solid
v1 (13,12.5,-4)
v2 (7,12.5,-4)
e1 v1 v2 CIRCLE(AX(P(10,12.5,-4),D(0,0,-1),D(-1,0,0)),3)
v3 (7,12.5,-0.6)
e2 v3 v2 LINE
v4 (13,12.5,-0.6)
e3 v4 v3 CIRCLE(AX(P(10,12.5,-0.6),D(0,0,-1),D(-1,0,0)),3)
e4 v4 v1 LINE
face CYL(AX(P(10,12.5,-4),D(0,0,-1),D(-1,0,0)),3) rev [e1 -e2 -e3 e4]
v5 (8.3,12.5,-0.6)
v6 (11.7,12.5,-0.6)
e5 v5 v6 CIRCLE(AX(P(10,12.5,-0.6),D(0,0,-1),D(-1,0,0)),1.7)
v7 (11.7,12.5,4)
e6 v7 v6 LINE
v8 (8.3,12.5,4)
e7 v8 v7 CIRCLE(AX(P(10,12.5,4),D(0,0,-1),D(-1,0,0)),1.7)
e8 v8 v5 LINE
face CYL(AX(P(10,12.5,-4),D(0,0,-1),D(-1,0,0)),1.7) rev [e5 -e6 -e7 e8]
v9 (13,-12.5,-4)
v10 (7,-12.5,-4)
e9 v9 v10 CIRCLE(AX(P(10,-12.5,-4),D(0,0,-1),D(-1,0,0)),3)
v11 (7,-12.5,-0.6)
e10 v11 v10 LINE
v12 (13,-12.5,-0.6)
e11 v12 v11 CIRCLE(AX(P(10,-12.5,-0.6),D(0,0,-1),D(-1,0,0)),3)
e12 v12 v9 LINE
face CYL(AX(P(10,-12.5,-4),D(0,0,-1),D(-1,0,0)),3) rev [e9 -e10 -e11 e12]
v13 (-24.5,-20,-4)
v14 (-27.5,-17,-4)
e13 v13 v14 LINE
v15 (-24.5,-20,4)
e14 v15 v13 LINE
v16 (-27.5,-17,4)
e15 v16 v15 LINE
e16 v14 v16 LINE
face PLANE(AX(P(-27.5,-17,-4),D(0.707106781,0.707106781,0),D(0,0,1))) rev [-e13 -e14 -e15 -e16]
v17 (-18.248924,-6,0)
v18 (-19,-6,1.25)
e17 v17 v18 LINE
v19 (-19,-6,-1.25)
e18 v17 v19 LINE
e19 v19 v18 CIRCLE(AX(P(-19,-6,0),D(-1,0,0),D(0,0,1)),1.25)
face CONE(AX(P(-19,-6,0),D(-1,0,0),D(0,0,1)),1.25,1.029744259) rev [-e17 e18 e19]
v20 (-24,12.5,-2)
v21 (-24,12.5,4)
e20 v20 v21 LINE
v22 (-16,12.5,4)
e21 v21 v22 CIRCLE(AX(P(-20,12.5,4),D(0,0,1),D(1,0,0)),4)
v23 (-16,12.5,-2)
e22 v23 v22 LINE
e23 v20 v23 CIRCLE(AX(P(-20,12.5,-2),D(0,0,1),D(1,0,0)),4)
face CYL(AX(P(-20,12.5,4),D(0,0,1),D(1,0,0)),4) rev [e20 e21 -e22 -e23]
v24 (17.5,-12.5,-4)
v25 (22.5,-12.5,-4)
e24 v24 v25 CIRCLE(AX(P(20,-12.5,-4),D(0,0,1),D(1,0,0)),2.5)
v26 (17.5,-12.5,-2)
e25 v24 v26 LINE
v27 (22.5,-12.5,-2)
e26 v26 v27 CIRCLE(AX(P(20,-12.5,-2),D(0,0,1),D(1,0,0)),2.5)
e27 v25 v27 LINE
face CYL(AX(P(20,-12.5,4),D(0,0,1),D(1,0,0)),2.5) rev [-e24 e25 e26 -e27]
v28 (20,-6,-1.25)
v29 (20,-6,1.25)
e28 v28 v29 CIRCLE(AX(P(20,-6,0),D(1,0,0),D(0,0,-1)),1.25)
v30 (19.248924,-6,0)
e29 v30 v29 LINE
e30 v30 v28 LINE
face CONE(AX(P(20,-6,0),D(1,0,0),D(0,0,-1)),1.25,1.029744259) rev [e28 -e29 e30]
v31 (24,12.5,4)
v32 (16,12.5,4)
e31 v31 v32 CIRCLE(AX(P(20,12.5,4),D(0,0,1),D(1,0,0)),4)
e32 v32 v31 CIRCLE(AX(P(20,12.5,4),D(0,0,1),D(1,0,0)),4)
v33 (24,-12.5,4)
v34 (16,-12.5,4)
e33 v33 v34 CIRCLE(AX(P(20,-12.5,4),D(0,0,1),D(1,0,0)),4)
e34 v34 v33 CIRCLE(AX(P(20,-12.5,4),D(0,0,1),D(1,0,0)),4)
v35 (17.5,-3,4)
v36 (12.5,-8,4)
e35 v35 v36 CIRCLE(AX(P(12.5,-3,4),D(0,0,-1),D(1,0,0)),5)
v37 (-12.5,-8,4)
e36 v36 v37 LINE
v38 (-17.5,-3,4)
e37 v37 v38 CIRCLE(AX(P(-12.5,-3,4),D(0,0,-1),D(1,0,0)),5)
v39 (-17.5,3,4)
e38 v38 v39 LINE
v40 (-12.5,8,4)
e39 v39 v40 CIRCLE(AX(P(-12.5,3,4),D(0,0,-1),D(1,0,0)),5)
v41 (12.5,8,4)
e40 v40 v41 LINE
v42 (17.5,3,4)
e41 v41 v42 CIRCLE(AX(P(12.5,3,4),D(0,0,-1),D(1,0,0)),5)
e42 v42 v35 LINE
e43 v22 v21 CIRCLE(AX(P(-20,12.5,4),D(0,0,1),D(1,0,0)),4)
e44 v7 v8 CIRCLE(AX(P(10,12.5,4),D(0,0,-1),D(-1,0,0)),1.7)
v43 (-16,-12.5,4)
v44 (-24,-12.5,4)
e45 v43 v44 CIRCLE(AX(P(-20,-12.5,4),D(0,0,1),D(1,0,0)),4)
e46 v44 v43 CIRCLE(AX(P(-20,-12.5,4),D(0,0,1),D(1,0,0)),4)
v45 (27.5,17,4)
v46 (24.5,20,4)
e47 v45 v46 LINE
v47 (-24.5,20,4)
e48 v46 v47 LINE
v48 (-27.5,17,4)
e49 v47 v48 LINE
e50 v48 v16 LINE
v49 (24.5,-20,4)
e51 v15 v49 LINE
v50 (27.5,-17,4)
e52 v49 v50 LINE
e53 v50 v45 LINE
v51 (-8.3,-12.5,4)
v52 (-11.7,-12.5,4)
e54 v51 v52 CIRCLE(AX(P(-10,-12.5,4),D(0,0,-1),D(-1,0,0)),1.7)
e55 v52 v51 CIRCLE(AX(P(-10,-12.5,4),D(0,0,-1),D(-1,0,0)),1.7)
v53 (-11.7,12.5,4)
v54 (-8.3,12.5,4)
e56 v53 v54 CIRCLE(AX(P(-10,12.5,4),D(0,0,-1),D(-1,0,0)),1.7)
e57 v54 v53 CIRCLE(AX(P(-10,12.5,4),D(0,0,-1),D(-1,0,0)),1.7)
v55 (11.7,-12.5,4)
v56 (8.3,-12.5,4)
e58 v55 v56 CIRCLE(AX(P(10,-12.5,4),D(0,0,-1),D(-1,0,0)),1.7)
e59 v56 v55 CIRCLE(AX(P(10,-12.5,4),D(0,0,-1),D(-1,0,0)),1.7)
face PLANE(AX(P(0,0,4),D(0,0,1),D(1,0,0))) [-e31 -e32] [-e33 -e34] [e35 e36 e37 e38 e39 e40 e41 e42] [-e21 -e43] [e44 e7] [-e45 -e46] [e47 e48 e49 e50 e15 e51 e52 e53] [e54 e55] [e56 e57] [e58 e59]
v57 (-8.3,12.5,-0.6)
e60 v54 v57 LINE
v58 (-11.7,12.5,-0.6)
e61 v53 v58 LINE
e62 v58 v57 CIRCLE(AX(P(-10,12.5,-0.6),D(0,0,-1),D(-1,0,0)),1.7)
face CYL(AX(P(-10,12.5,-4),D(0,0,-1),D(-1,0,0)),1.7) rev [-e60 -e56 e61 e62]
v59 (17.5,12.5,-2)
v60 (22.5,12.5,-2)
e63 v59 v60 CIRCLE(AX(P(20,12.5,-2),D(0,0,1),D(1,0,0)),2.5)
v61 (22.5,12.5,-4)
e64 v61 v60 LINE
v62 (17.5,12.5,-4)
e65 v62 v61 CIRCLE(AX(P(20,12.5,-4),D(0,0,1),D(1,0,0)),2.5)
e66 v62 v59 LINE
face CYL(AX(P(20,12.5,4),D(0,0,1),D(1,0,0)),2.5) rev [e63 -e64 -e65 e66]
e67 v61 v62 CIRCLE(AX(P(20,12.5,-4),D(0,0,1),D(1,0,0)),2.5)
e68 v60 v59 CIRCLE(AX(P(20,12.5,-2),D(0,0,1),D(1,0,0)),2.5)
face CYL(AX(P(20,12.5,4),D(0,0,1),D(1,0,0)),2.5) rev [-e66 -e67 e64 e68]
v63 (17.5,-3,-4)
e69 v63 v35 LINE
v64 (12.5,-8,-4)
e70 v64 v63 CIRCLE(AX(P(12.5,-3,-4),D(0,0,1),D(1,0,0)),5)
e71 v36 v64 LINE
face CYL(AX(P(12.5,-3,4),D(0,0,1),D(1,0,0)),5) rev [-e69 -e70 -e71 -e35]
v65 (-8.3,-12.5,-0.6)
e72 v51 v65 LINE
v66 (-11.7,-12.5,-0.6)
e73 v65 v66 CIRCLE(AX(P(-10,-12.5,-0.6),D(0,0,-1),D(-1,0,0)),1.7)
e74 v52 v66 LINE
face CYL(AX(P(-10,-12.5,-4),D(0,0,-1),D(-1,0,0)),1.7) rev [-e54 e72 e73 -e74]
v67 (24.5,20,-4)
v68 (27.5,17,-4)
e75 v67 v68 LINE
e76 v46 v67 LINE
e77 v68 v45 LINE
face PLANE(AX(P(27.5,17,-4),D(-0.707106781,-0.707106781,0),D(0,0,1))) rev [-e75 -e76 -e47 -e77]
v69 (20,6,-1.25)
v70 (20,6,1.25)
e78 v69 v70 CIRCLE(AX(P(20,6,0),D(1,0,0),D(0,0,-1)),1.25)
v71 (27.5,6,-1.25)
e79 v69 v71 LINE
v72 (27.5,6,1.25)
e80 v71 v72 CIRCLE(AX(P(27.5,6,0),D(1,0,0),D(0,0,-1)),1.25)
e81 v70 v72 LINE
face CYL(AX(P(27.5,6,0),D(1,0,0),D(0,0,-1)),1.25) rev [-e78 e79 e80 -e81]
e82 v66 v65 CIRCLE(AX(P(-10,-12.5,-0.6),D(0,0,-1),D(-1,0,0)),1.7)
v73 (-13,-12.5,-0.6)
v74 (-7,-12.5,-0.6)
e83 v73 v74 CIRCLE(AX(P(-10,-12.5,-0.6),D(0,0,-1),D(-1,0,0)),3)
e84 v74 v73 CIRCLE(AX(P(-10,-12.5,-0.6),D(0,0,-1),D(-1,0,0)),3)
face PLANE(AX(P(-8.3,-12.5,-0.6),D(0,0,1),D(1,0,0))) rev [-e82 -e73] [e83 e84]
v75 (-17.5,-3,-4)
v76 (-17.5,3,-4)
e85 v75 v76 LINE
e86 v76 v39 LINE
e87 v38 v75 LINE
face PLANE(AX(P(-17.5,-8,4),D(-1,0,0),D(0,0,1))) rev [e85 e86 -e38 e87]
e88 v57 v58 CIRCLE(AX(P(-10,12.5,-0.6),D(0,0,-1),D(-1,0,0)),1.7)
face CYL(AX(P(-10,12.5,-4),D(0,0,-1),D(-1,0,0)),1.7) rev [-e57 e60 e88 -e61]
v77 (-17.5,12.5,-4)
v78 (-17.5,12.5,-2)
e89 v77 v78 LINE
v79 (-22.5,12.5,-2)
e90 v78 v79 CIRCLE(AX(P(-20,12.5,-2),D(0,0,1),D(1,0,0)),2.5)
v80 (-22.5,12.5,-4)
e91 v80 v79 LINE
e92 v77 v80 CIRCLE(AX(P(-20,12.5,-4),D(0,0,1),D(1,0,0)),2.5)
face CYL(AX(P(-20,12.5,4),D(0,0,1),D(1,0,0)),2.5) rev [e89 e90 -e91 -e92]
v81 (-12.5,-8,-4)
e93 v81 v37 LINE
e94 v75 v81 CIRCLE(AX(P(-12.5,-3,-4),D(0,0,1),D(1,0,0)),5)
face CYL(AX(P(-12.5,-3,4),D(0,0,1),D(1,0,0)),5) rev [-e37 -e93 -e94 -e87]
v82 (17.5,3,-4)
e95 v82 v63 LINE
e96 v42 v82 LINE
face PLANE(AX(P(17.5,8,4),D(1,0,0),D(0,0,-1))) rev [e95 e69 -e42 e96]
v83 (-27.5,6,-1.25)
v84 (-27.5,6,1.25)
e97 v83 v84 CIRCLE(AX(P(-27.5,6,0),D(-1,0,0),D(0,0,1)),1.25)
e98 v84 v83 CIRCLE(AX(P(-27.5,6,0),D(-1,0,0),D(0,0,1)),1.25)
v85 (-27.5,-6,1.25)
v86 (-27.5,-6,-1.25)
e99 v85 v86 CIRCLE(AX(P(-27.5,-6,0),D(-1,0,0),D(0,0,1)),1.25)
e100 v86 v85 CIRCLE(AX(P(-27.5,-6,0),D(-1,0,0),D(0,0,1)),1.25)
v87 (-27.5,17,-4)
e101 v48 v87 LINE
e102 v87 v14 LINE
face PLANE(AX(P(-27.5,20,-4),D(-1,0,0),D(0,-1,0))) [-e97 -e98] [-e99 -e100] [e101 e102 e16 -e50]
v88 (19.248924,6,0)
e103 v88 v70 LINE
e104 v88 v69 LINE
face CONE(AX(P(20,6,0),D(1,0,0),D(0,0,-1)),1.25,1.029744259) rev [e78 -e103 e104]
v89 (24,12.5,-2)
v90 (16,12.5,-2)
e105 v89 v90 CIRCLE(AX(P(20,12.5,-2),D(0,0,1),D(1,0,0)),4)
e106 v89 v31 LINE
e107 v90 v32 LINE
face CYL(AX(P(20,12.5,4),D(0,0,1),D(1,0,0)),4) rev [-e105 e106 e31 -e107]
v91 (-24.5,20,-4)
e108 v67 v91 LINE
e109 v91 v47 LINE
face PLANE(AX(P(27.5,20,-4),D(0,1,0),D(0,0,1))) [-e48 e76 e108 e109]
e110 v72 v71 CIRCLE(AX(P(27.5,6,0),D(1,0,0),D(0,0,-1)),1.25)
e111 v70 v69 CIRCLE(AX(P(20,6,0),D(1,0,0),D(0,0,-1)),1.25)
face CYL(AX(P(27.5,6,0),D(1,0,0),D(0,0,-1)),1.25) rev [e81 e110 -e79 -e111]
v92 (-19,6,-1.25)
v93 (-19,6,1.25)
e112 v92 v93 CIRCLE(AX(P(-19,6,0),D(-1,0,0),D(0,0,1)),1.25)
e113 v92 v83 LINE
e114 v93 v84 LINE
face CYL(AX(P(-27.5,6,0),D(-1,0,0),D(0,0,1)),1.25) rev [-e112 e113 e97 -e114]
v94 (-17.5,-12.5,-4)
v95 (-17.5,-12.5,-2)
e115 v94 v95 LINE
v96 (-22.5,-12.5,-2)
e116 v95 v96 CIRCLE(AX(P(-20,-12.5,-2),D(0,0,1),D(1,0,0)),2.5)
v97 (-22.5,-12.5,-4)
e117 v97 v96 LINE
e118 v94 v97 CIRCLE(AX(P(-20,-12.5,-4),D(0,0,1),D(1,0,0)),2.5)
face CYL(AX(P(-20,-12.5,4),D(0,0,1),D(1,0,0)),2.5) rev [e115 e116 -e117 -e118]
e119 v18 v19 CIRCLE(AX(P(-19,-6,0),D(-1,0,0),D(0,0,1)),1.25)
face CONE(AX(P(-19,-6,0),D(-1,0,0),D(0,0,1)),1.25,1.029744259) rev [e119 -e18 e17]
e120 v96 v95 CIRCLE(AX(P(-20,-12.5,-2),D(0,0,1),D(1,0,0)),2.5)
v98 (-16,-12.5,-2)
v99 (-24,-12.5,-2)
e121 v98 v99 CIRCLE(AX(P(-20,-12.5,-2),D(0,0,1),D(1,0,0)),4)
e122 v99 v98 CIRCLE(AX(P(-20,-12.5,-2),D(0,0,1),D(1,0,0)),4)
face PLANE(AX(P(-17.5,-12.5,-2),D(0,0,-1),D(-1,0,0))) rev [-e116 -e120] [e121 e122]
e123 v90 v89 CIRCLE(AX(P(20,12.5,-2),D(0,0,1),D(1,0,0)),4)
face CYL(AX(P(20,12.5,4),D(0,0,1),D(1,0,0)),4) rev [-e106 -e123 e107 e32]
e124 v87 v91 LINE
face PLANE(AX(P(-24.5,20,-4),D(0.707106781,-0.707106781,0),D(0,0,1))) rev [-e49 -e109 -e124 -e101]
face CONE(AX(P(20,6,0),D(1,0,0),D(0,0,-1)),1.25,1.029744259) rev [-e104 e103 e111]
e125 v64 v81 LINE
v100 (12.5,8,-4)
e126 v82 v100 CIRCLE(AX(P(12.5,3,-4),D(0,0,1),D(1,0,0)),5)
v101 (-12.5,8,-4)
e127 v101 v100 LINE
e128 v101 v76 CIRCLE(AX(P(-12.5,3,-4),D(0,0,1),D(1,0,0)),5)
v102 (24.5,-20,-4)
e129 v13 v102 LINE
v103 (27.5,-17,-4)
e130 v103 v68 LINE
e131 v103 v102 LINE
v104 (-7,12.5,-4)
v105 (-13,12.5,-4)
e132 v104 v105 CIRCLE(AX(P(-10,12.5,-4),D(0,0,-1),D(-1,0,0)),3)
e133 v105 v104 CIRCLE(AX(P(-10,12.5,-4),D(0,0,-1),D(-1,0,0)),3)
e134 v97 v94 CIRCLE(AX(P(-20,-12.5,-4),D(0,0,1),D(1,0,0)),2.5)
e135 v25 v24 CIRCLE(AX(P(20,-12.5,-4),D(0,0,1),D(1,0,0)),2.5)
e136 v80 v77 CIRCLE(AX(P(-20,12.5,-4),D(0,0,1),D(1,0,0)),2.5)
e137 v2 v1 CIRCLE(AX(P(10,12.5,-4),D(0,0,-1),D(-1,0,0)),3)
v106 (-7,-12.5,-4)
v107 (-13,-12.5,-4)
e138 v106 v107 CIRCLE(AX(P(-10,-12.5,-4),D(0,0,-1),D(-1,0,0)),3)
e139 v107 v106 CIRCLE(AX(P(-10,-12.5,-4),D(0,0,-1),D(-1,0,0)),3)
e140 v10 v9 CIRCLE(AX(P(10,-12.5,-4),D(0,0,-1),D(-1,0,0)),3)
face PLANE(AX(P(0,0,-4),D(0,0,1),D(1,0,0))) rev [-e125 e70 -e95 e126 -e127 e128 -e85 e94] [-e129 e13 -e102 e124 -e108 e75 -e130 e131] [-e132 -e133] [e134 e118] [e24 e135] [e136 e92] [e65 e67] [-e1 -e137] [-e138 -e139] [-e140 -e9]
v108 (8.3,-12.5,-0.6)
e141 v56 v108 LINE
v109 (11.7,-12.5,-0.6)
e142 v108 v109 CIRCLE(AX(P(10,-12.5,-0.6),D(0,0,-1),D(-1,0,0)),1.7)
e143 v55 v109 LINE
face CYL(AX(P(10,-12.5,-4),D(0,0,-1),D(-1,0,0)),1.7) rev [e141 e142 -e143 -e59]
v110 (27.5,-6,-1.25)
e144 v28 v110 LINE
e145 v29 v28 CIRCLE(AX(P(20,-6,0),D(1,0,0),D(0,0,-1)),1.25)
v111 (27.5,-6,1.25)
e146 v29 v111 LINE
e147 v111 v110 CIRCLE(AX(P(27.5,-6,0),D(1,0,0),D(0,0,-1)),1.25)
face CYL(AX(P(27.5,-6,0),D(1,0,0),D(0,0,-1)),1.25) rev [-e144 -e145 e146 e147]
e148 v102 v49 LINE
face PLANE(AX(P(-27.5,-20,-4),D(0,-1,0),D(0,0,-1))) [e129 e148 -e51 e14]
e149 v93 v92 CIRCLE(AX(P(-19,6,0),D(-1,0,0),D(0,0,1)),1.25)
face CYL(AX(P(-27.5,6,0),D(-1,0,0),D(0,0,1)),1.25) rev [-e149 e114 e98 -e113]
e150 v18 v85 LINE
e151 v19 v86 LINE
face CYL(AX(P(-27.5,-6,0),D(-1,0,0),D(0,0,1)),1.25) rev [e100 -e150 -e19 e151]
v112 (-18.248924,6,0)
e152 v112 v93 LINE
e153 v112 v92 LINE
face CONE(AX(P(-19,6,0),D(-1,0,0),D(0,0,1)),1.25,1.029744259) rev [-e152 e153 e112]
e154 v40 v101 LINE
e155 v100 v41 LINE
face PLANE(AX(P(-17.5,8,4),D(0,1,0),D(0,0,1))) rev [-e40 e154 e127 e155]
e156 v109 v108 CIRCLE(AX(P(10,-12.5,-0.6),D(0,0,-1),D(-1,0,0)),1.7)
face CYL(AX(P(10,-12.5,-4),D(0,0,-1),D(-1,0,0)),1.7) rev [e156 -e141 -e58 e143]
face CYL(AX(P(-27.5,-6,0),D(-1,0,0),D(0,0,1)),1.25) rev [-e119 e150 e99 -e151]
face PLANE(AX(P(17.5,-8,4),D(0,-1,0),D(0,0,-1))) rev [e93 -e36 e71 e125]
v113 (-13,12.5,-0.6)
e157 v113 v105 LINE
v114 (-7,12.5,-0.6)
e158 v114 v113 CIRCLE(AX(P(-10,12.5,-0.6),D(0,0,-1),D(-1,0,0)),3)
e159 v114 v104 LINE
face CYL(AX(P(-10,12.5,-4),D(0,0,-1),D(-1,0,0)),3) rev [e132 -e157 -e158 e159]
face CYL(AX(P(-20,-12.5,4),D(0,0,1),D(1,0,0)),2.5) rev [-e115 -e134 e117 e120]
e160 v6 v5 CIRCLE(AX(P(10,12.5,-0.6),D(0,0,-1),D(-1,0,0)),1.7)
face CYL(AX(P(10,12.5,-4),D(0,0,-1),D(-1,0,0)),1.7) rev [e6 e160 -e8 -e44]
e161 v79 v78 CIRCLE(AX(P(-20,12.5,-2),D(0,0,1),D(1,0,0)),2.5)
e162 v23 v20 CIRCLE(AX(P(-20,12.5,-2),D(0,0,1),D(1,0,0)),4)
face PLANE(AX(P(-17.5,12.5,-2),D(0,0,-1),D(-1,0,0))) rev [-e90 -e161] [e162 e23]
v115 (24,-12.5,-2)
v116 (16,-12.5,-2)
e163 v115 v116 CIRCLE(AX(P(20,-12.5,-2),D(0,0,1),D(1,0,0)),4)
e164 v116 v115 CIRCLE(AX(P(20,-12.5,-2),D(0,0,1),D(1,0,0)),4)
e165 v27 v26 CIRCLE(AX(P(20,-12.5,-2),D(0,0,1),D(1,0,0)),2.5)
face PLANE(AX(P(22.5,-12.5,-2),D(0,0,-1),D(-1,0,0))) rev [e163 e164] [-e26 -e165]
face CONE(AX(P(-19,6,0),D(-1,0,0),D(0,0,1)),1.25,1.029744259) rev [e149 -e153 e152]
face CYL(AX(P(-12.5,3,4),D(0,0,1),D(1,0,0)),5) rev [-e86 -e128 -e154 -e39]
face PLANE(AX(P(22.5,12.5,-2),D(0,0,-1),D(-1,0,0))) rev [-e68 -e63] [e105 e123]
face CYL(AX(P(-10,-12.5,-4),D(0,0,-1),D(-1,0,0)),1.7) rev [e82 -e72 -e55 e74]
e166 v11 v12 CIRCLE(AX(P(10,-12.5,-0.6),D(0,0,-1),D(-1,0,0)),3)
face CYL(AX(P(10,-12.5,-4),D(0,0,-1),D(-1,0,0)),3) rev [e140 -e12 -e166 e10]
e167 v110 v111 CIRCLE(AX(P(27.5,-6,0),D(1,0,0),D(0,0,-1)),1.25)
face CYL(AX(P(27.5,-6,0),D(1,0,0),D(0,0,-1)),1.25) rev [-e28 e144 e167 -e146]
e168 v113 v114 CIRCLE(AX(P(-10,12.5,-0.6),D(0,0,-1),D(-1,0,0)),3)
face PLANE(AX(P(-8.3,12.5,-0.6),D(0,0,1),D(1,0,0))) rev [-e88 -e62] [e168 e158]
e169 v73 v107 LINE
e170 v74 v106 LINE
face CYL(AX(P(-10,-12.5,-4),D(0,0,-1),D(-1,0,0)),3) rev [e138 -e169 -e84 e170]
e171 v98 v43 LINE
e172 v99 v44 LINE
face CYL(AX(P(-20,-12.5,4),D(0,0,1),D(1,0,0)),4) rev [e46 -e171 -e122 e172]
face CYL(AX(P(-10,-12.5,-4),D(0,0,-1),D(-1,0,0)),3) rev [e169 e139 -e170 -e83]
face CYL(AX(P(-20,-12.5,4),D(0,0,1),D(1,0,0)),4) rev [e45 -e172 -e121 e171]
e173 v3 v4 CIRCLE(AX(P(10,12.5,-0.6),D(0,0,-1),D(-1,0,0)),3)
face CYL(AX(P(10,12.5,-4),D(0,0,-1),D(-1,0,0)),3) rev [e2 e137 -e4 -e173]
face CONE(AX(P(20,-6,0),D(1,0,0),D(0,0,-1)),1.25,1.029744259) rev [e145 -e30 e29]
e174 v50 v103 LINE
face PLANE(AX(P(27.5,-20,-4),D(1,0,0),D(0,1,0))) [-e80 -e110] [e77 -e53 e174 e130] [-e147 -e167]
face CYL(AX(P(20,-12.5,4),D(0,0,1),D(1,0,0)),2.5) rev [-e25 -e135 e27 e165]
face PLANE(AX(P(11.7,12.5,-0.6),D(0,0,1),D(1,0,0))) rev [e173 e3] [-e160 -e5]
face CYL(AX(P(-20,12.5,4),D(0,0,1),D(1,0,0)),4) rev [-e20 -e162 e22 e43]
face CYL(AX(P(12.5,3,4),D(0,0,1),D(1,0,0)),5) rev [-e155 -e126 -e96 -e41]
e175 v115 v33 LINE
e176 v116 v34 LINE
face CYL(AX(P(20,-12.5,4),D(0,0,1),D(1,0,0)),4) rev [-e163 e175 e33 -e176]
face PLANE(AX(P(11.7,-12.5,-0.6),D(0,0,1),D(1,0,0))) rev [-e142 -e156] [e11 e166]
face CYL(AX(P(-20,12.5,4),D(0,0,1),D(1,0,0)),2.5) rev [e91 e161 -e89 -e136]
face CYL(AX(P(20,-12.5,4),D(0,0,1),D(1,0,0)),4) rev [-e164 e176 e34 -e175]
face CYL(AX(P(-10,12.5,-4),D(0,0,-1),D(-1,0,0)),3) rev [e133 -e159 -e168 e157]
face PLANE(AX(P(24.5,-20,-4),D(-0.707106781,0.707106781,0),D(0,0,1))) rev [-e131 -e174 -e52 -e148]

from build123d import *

# Parameters (mm, degrees)
SKETCH_1_W                   = 55
SKETCH_1_H                   = 40
EXTRUDE_1_DEPTH              = 8
SKETCH_2_W                   = 35
SKETCH_2_H                   = 16
CUT_EXTRUDE_1_DEPTH          = 35.932076949
HOLE_WIZARD_M3_1_D           = 3.4
HOLE_WIZARD_M3_1_CBORE_D     = 6
HOLE_WIZARD_M3_1_CBORE_DEPTH = 3.4
HOLE_WIZARD_M3_1_2_D         = 2.5
HOLE_WIZARD_M3_1_2_DEPTH     = 7.5
HOLE_WIZARD_M3_1_2_TIP       = 0.751075774
M8X1_0_1_D                   = 5
M8X1_0_1_CBORE_D             = 8
M8X1_0_1_CBORE_DEPTH         = 6
HOLE_WIZARD_M3_2_D           = 2.5
HOLE_WIZARD_M3_2_DEPTH       = 8.5
HOLE_WIZARD_M3_2_TIP         = 0.751075774
CHAMFER_1_SIZE               = 3
FILLET_1_R                   = 5


with BuildPart() as part:
    # 草图1 → 凸台-拉伸1 (new body)
    with BuildSketch(Plane.XY.offset(4)):
        Rectangle(SKETCH_1_W, SKETCH_1_H)
    extrude(amount=-EXTRUDE_1_DEPTH)

    # 草图2 → 切除-拉伸1 (cut, through all)
    with BuildSketch(Plane(origin=(0, 0, -4), x_dir=(-1, 0, 0), z_dir=(0, 0, -1))):
        Rectangle(SKETCH_2_W, SKETCH_2_H)
    extrude(amount=-CUT_EXTRUDE_1_DEPTH, mode=Mode.SUBTRACT)

    # Hole Wizard M3 _1 (through all)
    with Locations(Plane(origin=(0, 0, -4), x_dir=(-1, 0, 0), z_dir=(0, 0, -1))):
        with Locations((10, -12.5), (-10, -12.5), (10, 12.5), (-10, 12.5)):
            CounterBoreHole(HOLE_WIZARD_M3_1_D / 2, HOLE_WIZARD_M3_1_CBORE_D / 2, HOLE_WIZARD_M3_1_CBORE_DEPTH)

    # Hole Wizard M3 _1 2
    with Locations(Plane(origin=(27.5, 0, 0), x_dir=(0, 0, -1), z_dir=(1, 0, 0))):
        with Locations((0, 6), (0, -6)):
            Hole(HOLE_WIZARD_M3_1_2_D / 2, depth=HOLE_WIZARD_M3_1_2_DEPTH)
            with Locations((0, 0, -(HOLE_WIZARD_M3_1_2_DEPTH + HOLE_WIZARD_M3_1_2_TIP / 2))):  # 118° drill point
                Cone(0, HOLE_WIZARD_M3_1_2_D / 2, HOLE_WIZARD_M3_1_2_TIP, mode=Mode.SUBTRACT)

    # M8x1.0 螺纹孔1 (through all)
    with Locations(Plane.XY.offset(4)):
        with Locations((-20, 12.5), (-20, -12.5), (20, 12.5), (20, -12.5)):
            CounterBoreHole(M8X1_0_1_D / 2, M8X1_0_1_CBORE_D / 2, M8X1_0_1_CBORE_DEPTH)

    # M3 螺纹孔2
    with Locations(Plane.ZY.offset(27.5)):
        with Locations((0, 6), (0, -6)):
            Hole(HOLE_WIZARD_M3_2_D / 2, depth=HOLE_WIZARD_M3_2_DEPTH)
            with Locations((0, 0, -(HOLE_WIZARD_M3_2_DEPTH + HOLE_WIZARD_M3_2_TIP / 2))):  # 118° drill point
                Cone(0, HOLE_WIZARD_M3_2_D / 2, HOLE_WIZARD_M3_2_TIP, mode=Mode.SUBTRACT)

    # 倒角1
    chamfer_1_edges = [part.edges().sort_by_distance(p)[0] for p in [
        (27.5, 20, 0),
        (27.5, -20, 0),
        (-27.5, -20, 0),
        (-27.5, 20, 0),
    ]]
    chamfer(chamfer_1_edges, length=CHAMFER_1_SIZE)

    # 圆角1
    fillet_1_edges = [part.edges().sort_by_distance(p)[0] for p in [
        (-17.5, -8, 0),
        (17.5, -8, 0),
        (17.5, 8, 0),
        (-17.5, 8, 0),
    ]]
    fillet(fillet_1_edges, radius=FILLET_1_R)


solid = part.part
